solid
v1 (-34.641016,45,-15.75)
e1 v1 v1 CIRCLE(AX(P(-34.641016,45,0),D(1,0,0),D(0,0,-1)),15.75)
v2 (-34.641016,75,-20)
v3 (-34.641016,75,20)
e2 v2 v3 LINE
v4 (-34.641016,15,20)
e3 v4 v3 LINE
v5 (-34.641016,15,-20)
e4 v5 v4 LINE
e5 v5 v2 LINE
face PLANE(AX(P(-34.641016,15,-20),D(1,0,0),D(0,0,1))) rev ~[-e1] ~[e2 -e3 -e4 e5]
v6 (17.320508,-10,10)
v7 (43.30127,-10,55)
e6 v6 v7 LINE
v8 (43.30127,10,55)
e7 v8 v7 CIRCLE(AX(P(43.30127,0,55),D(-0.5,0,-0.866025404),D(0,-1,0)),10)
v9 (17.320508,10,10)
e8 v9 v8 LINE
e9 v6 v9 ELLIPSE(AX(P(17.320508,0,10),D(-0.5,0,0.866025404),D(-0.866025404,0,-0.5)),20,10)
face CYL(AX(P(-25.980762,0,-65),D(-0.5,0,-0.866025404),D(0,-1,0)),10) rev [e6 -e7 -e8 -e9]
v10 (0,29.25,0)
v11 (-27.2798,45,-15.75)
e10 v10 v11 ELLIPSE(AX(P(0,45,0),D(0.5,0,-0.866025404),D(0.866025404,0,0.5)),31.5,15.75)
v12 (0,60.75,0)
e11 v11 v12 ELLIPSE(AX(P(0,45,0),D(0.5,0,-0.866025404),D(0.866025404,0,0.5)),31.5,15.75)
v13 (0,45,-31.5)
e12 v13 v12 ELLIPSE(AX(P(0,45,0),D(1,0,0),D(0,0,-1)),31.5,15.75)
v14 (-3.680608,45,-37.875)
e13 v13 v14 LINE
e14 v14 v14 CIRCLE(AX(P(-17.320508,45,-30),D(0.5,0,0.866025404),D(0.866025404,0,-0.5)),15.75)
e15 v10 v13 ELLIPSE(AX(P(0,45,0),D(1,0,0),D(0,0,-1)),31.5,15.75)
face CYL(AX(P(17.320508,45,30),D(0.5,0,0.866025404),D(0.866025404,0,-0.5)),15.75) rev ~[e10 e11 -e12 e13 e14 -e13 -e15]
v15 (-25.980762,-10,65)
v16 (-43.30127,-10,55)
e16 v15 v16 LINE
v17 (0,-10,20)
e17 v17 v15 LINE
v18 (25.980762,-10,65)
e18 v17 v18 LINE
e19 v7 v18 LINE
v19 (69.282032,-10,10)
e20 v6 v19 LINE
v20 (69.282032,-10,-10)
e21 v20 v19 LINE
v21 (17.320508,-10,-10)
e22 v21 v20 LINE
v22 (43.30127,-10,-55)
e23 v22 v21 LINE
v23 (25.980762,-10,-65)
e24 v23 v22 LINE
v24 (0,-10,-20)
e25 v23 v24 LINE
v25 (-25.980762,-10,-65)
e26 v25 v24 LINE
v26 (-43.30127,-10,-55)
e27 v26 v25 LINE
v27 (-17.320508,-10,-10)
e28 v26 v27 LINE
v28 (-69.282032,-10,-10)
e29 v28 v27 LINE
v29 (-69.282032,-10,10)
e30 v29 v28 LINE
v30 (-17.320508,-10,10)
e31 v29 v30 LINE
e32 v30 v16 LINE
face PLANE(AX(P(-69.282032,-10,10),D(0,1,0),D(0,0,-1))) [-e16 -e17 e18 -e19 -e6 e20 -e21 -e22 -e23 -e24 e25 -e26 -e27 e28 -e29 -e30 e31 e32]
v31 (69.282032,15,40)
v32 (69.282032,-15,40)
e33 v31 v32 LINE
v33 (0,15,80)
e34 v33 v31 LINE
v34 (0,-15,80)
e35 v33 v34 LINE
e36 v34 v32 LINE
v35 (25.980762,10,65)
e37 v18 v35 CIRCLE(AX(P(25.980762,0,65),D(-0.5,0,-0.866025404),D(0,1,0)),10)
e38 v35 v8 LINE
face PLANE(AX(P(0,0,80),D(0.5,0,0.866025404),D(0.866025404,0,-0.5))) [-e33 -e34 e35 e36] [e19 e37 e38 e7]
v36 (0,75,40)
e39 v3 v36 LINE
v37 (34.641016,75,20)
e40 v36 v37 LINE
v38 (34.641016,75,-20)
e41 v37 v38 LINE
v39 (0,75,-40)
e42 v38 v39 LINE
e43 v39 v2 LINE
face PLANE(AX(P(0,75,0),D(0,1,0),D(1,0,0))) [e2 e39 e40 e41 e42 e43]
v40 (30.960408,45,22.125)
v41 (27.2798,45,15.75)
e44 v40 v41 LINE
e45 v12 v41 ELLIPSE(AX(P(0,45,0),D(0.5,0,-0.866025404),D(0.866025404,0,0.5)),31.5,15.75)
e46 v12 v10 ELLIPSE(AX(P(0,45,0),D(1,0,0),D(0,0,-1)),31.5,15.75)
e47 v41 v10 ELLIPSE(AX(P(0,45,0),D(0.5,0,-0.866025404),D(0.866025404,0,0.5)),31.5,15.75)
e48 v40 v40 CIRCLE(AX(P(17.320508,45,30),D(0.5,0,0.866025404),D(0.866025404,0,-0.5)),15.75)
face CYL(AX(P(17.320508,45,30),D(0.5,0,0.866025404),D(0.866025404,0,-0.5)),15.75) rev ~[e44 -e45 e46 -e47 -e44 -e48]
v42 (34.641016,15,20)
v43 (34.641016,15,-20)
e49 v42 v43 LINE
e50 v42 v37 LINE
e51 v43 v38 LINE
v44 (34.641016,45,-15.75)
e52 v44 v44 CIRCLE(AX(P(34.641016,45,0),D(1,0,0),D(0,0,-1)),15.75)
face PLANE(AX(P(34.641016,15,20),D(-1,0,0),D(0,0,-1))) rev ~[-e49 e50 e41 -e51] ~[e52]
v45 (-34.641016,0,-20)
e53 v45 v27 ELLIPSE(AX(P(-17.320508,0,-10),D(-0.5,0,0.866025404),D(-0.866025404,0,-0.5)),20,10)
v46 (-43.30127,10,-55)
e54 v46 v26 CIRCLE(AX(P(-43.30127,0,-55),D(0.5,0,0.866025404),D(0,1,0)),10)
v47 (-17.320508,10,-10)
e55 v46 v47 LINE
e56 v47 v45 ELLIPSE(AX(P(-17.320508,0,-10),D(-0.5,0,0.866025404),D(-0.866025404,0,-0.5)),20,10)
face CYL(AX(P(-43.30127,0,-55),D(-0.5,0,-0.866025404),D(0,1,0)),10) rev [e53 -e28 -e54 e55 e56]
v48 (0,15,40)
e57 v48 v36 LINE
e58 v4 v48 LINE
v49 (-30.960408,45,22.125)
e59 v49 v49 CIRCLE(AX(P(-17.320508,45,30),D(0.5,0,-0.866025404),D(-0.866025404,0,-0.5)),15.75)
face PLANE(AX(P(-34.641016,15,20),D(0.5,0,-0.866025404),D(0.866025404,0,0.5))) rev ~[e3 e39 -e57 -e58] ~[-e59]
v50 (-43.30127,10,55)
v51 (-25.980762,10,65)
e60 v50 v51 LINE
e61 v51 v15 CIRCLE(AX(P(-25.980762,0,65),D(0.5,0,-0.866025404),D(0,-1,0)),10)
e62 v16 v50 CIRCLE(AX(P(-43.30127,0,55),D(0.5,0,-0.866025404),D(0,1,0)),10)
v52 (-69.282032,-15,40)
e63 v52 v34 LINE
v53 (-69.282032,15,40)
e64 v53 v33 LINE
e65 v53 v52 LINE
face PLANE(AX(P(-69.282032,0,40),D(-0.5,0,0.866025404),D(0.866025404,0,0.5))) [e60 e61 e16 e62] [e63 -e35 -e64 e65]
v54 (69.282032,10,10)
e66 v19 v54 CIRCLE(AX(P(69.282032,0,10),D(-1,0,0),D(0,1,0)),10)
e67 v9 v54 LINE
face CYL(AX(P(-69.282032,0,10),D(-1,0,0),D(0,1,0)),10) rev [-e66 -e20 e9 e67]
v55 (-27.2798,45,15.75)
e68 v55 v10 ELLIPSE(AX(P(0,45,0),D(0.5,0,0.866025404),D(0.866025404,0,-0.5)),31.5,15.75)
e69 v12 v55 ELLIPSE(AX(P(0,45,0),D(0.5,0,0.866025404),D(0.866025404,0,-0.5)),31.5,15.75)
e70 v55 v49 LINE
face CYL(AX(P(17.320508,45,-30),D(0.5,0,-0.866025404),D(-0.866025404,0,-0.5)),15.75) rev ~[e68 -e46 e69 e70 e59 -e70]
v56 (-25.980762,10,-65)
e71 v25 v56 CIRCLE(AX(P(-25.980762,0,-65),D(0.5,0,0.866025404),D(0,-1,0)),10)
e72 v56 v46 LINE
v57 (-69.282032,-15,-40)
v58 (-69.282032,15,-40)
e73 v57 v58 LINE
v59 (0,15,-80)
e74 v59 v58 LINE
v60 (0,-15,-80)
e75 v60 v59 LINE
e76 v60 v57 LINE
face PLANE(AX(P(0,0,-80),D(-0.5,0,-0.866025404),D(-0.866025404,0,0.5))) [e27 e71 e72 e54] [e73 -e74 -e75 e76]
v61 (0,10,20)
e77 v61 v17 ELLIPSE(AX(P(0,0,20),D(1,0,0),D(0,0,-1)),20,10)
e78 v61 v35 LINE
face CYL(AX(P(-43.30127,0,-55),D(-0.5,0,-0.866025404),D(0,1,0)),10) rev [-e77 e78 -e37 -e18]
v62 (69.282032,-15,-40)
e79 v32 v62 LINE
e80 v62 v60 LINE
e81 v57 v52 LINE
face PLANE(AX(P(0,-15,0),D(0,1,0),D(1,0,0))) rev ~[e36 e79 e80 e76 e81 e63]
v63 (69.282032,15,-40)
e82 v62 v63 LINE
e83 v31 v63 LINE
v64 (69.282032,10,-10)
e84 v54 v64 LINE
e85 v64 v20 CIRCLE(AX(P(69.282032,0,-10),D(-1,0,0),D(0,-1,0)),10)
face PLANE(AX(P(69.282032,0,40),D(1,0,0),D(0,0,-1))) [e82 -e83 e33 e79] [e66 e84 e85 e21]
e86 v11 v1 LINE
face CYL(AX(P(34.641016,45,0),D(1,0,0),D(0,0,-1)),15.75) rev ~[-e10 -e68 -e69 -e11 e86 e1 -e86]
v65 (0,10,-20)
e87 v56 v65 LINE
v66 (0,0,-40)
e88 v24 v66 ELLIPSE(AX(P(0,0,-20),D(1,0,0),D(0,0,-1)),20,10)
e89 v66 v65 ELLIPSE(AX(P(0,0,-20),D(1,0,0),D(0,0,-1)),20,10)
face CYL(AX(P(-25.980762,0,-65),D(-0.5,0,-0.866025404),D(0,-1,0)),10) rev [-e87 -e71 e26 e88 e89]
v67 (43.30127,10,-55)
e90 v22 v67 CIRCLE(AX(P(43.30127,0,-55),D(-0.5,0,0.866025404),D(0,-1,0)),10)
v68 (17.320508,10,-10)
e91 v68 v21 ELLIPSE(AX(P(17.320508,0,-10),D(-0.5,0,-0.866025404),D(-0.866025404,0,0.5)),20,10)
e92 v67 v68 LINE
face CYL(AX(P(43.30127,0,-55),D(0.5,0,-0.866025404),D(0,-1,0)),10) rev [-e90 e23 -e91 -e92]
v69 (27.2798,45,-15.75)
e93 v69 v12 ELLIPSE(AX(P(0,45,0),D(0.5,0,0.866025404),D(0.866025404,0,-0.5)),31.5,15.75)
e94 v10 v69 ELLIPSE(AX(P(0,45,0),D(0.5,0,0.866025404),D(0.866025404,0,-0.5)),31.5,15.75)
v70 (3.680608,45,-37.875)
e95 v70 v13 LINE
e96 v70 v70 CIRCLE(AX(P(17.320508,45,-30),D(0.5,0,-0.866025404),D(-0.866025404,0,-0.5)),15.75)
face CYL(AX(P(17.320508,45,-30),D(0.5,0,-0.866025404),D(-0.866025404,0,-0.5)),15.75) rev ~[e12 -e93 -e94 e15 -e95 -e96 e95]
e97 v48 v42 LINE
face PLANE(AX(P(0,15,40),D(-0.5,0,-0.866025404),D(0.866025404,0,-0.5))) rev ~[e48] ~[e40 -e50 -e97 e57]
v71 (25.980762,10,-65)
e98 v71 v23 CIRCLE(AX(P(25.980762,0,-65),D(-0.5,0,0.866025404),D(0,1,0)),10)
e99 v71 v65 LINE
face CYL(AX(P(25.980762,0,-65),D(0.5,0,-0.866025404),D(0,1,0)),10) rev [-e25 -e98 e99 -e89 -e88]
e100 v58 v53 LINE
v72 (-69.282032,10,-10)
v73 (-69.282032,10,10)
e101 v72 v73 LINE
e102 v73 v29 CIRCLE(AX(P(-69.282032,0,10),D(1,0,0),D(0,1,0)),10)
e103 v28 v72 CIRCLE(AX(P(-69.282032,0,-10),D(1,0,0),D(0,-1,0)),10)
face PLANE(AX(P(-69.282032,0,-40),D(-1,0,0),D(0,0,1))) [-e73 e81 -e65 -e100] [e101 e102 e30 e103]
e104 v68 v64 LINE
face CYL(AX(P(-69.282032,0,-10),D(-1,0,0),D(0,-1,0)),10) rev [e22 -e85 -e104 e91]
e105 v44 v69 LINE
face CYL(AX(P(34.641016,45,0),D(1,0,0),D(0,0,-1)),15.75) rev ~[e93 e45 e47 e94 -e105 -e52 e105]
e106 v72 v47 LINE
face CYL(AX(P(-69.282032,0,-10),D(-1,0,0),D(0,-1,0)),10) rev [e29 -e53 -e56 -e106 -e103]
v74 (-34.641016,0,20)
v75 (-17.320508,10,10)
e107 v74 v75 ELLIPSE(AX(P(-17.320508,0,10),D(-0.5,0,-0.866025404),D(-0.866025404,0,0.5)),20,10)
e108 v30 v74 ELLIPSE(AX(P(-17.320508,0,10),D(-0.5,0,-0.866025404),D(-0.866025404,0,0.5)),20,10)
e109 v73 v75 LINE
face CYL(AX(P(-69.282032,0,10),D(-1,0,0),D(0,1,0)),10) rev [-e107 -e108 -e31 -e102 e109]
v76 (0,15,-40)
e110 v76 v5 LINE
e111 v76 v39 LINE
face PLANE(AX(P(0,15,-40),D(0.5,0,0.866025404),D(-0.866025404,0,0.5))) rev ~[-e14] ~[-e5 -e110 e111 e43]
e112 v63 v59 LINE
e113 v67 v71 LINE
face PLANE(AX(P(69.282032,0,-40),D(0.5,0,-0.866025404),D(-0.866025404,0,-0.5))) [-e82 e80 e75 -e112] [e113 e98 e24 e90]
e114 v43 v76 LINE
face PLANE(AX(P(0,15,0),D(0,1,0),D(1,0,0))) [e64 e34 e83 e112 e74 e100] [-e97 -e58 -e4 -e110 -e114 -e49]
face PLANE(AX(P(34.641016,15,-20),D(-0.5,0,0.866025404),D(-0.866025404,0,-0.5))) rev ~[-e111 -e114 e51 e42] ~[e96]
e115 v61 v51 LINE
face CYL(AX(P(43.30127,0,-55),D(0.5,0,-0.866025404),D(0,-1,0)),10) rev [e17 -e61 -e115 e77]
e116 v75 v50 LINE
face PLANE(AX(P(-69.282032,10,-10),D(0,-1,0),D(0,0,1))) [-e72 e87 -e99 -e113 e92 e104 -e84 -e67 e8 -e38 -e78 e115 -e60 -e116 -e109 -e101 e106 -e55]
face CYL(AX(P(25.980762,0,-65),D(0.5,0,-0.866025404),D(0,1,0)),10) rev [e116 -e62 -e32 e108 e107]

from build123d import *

# Parameters (mm, degrees)
HEX_BASE_DEPTH          = 15
SIDE_SLOT_1_20X10_DEPTH = 161.7015868
SIDE_SLOT_2_20X10_DEPTH = 176
SIDE_SLOT_3_20X10_DEPTH = 176
HEX_BOSS_DEPTH          = 60
CROSS_HOLE_1_SKETCH_R   = 15.75
CROSS_HOLE_1_31_5_DEPTH = 152.079449297
CROSS_HOLE_2_SKETCH_R   = 15.75
CROSS_HOLE_2_31_5_DEPTH = 159.823801743
CROSS_HOLE_3_SKETCH_R   = 15.75
CROSS_HOLE_3_31_5_DEPTH = 159.823801743


with BuildPart() as part:
    # Hex Base Sketch → Hex Base (new, symmetric)
    with BuildSketch(Plane(origin=(0, 0, 0), x_dir=(1, 0, 0), z_dir=(0, 1, 0))):
        Polygon((69.282032303, -40), (69.282032303, 40), (0, 80), (-69.282032303, 40), (-69.282032303, -40), (0, -80), align=None)
    extrude(amount=HEX_BASE_DEPTH, both=True)

    # Side Slot 1 Sketch → Side Slot 1 20x10 (cut, through all)
    with BuildSketch(Plane.ZY.offset(69.282032303)):
        with BuildLine():
            Line((-10, 10), (10, 10))
            ThreePointArc((10, 10), (20, 0), (10, -10))
            Line((10, -10), (-10, -10))
            ThreePointArc((-10, -10), (-20, 0), (-10, 10))
        make_face()
    extrude(amount=-SIDE_SLOT_1_20X10_DEPTH, mode=Mode.SUBTRACT)

    # Side Slot 2 Sketch → Side Slot 2 20x10 (cut, through all)
    with BuildSketch(Plane(origin=(34.641016151, 0, -60), x_dir=(-0.8660254037844386, 0, -0.5000000000000003), z_dir=(0.5000000000000002, 0, -0.8660254037844385))):
        with BuildLine():
            Line((-10, 10), (10, 10))
            ThreePointArc((10, 10), (20, 0), (10, -10))
            Line((10, -10), (-10, -10))
            ThreePointArc((-10, -10), (-20, 0), (-10, 10))
        make_face()
    extrude(amount=-SIDE_SLOT_2_20X10_DEPTH, mode=Mode.SUBTRACT)

    # Side Slot 3 Sketch → Side Slot 3 20x10 (cut, through all)
    with BuildSketch(Plane(origin=(-34.641016151, 0, -60), x_dir=(-0.8660254037844388, 0, 0.49999999999999983), z_dir=(-0.4999999999999998, 0, -0.8660254037844387))):
        with BuildLine():
            Line((-10, 10), (10, 10))
            ThreePointArc((10, 10), (20, 0), (10, -10))
            Line((10, -10), (-10, -10))
            ThreePointArc((-10, -10), (-20, 0), (-10, 10))
        make_face()
    extrude(amount=-SIDE_SLOT_3_20X10_DEPTH, mode=Mode.SUBTRACT)

    # Hex Boss Sketch → Hex Boss (add)
    with BuildSketch(Plane(origin=(0, 15, 0), x_dir=(1, 0, 0), z_dir=(0, 1, 0))):
        Polygon((34.641016151, -20), (34.641016151, 20), (0, 40), (-34.641016151, 20), (-34.641016151, -20), (0, -40), align=None)
    extrude(amount=HEX_BOSS_DEPTH)

    # Cross Hole 1 Sketch → Cross Hole 1 Ø31.5 (cut, through all)
    with BuildSketch(Plane(origin=(34.641016151, 0, 0), x_dir=(0, 0, -1), z_dir=(1, 0, 0))):
        with Locations((0, 45)):
            Circle(CROSS_HOLE_1_SKETCH_R)
    extrude(amount=-CROSS_HOLE_1_31_5_DEPTH, mode=Mode.SUBTRACT)

    # Cross Hole 2 Sketch → Cross Hole 2 Ø31.5 (cut, through all)
    with BuildSketch(Plane(origin=(17.320508076, 0, -30), x_dir=(-0.8660254037844384, 0, -0.5000000000000004), z_dir=(0.5000000000000004, 0, -0.8660254037844384))):
        with Locations((0, 45)):
            Circle(CROSS_HOLE_2_SKETCH_R)
    extrude(amount=-CROSS_HOLE_2_31_5_DEPTH, mode=Mode.SUBTRACT)

    # Cross Hole 3 Sketch → Cross Hole 3 Ø31.5 (cut, through all)
    with BuildSketch(Plane(origin=(17.320508076, 0, 30), x_dir=(0.8660254037844388, 0, -0.4999999999999997), z_dir=(0.4999999999999997, 0, 0.8660254037844388))):
        with Locations((0, 45)):
            Circle(CROSS_HOLE_3_SKETCH_R)
    extrude(amount=-CROSS_HOLE_3_31_5_DEPTH, mode=Mode.SUBTRACT)


solid = part.part
